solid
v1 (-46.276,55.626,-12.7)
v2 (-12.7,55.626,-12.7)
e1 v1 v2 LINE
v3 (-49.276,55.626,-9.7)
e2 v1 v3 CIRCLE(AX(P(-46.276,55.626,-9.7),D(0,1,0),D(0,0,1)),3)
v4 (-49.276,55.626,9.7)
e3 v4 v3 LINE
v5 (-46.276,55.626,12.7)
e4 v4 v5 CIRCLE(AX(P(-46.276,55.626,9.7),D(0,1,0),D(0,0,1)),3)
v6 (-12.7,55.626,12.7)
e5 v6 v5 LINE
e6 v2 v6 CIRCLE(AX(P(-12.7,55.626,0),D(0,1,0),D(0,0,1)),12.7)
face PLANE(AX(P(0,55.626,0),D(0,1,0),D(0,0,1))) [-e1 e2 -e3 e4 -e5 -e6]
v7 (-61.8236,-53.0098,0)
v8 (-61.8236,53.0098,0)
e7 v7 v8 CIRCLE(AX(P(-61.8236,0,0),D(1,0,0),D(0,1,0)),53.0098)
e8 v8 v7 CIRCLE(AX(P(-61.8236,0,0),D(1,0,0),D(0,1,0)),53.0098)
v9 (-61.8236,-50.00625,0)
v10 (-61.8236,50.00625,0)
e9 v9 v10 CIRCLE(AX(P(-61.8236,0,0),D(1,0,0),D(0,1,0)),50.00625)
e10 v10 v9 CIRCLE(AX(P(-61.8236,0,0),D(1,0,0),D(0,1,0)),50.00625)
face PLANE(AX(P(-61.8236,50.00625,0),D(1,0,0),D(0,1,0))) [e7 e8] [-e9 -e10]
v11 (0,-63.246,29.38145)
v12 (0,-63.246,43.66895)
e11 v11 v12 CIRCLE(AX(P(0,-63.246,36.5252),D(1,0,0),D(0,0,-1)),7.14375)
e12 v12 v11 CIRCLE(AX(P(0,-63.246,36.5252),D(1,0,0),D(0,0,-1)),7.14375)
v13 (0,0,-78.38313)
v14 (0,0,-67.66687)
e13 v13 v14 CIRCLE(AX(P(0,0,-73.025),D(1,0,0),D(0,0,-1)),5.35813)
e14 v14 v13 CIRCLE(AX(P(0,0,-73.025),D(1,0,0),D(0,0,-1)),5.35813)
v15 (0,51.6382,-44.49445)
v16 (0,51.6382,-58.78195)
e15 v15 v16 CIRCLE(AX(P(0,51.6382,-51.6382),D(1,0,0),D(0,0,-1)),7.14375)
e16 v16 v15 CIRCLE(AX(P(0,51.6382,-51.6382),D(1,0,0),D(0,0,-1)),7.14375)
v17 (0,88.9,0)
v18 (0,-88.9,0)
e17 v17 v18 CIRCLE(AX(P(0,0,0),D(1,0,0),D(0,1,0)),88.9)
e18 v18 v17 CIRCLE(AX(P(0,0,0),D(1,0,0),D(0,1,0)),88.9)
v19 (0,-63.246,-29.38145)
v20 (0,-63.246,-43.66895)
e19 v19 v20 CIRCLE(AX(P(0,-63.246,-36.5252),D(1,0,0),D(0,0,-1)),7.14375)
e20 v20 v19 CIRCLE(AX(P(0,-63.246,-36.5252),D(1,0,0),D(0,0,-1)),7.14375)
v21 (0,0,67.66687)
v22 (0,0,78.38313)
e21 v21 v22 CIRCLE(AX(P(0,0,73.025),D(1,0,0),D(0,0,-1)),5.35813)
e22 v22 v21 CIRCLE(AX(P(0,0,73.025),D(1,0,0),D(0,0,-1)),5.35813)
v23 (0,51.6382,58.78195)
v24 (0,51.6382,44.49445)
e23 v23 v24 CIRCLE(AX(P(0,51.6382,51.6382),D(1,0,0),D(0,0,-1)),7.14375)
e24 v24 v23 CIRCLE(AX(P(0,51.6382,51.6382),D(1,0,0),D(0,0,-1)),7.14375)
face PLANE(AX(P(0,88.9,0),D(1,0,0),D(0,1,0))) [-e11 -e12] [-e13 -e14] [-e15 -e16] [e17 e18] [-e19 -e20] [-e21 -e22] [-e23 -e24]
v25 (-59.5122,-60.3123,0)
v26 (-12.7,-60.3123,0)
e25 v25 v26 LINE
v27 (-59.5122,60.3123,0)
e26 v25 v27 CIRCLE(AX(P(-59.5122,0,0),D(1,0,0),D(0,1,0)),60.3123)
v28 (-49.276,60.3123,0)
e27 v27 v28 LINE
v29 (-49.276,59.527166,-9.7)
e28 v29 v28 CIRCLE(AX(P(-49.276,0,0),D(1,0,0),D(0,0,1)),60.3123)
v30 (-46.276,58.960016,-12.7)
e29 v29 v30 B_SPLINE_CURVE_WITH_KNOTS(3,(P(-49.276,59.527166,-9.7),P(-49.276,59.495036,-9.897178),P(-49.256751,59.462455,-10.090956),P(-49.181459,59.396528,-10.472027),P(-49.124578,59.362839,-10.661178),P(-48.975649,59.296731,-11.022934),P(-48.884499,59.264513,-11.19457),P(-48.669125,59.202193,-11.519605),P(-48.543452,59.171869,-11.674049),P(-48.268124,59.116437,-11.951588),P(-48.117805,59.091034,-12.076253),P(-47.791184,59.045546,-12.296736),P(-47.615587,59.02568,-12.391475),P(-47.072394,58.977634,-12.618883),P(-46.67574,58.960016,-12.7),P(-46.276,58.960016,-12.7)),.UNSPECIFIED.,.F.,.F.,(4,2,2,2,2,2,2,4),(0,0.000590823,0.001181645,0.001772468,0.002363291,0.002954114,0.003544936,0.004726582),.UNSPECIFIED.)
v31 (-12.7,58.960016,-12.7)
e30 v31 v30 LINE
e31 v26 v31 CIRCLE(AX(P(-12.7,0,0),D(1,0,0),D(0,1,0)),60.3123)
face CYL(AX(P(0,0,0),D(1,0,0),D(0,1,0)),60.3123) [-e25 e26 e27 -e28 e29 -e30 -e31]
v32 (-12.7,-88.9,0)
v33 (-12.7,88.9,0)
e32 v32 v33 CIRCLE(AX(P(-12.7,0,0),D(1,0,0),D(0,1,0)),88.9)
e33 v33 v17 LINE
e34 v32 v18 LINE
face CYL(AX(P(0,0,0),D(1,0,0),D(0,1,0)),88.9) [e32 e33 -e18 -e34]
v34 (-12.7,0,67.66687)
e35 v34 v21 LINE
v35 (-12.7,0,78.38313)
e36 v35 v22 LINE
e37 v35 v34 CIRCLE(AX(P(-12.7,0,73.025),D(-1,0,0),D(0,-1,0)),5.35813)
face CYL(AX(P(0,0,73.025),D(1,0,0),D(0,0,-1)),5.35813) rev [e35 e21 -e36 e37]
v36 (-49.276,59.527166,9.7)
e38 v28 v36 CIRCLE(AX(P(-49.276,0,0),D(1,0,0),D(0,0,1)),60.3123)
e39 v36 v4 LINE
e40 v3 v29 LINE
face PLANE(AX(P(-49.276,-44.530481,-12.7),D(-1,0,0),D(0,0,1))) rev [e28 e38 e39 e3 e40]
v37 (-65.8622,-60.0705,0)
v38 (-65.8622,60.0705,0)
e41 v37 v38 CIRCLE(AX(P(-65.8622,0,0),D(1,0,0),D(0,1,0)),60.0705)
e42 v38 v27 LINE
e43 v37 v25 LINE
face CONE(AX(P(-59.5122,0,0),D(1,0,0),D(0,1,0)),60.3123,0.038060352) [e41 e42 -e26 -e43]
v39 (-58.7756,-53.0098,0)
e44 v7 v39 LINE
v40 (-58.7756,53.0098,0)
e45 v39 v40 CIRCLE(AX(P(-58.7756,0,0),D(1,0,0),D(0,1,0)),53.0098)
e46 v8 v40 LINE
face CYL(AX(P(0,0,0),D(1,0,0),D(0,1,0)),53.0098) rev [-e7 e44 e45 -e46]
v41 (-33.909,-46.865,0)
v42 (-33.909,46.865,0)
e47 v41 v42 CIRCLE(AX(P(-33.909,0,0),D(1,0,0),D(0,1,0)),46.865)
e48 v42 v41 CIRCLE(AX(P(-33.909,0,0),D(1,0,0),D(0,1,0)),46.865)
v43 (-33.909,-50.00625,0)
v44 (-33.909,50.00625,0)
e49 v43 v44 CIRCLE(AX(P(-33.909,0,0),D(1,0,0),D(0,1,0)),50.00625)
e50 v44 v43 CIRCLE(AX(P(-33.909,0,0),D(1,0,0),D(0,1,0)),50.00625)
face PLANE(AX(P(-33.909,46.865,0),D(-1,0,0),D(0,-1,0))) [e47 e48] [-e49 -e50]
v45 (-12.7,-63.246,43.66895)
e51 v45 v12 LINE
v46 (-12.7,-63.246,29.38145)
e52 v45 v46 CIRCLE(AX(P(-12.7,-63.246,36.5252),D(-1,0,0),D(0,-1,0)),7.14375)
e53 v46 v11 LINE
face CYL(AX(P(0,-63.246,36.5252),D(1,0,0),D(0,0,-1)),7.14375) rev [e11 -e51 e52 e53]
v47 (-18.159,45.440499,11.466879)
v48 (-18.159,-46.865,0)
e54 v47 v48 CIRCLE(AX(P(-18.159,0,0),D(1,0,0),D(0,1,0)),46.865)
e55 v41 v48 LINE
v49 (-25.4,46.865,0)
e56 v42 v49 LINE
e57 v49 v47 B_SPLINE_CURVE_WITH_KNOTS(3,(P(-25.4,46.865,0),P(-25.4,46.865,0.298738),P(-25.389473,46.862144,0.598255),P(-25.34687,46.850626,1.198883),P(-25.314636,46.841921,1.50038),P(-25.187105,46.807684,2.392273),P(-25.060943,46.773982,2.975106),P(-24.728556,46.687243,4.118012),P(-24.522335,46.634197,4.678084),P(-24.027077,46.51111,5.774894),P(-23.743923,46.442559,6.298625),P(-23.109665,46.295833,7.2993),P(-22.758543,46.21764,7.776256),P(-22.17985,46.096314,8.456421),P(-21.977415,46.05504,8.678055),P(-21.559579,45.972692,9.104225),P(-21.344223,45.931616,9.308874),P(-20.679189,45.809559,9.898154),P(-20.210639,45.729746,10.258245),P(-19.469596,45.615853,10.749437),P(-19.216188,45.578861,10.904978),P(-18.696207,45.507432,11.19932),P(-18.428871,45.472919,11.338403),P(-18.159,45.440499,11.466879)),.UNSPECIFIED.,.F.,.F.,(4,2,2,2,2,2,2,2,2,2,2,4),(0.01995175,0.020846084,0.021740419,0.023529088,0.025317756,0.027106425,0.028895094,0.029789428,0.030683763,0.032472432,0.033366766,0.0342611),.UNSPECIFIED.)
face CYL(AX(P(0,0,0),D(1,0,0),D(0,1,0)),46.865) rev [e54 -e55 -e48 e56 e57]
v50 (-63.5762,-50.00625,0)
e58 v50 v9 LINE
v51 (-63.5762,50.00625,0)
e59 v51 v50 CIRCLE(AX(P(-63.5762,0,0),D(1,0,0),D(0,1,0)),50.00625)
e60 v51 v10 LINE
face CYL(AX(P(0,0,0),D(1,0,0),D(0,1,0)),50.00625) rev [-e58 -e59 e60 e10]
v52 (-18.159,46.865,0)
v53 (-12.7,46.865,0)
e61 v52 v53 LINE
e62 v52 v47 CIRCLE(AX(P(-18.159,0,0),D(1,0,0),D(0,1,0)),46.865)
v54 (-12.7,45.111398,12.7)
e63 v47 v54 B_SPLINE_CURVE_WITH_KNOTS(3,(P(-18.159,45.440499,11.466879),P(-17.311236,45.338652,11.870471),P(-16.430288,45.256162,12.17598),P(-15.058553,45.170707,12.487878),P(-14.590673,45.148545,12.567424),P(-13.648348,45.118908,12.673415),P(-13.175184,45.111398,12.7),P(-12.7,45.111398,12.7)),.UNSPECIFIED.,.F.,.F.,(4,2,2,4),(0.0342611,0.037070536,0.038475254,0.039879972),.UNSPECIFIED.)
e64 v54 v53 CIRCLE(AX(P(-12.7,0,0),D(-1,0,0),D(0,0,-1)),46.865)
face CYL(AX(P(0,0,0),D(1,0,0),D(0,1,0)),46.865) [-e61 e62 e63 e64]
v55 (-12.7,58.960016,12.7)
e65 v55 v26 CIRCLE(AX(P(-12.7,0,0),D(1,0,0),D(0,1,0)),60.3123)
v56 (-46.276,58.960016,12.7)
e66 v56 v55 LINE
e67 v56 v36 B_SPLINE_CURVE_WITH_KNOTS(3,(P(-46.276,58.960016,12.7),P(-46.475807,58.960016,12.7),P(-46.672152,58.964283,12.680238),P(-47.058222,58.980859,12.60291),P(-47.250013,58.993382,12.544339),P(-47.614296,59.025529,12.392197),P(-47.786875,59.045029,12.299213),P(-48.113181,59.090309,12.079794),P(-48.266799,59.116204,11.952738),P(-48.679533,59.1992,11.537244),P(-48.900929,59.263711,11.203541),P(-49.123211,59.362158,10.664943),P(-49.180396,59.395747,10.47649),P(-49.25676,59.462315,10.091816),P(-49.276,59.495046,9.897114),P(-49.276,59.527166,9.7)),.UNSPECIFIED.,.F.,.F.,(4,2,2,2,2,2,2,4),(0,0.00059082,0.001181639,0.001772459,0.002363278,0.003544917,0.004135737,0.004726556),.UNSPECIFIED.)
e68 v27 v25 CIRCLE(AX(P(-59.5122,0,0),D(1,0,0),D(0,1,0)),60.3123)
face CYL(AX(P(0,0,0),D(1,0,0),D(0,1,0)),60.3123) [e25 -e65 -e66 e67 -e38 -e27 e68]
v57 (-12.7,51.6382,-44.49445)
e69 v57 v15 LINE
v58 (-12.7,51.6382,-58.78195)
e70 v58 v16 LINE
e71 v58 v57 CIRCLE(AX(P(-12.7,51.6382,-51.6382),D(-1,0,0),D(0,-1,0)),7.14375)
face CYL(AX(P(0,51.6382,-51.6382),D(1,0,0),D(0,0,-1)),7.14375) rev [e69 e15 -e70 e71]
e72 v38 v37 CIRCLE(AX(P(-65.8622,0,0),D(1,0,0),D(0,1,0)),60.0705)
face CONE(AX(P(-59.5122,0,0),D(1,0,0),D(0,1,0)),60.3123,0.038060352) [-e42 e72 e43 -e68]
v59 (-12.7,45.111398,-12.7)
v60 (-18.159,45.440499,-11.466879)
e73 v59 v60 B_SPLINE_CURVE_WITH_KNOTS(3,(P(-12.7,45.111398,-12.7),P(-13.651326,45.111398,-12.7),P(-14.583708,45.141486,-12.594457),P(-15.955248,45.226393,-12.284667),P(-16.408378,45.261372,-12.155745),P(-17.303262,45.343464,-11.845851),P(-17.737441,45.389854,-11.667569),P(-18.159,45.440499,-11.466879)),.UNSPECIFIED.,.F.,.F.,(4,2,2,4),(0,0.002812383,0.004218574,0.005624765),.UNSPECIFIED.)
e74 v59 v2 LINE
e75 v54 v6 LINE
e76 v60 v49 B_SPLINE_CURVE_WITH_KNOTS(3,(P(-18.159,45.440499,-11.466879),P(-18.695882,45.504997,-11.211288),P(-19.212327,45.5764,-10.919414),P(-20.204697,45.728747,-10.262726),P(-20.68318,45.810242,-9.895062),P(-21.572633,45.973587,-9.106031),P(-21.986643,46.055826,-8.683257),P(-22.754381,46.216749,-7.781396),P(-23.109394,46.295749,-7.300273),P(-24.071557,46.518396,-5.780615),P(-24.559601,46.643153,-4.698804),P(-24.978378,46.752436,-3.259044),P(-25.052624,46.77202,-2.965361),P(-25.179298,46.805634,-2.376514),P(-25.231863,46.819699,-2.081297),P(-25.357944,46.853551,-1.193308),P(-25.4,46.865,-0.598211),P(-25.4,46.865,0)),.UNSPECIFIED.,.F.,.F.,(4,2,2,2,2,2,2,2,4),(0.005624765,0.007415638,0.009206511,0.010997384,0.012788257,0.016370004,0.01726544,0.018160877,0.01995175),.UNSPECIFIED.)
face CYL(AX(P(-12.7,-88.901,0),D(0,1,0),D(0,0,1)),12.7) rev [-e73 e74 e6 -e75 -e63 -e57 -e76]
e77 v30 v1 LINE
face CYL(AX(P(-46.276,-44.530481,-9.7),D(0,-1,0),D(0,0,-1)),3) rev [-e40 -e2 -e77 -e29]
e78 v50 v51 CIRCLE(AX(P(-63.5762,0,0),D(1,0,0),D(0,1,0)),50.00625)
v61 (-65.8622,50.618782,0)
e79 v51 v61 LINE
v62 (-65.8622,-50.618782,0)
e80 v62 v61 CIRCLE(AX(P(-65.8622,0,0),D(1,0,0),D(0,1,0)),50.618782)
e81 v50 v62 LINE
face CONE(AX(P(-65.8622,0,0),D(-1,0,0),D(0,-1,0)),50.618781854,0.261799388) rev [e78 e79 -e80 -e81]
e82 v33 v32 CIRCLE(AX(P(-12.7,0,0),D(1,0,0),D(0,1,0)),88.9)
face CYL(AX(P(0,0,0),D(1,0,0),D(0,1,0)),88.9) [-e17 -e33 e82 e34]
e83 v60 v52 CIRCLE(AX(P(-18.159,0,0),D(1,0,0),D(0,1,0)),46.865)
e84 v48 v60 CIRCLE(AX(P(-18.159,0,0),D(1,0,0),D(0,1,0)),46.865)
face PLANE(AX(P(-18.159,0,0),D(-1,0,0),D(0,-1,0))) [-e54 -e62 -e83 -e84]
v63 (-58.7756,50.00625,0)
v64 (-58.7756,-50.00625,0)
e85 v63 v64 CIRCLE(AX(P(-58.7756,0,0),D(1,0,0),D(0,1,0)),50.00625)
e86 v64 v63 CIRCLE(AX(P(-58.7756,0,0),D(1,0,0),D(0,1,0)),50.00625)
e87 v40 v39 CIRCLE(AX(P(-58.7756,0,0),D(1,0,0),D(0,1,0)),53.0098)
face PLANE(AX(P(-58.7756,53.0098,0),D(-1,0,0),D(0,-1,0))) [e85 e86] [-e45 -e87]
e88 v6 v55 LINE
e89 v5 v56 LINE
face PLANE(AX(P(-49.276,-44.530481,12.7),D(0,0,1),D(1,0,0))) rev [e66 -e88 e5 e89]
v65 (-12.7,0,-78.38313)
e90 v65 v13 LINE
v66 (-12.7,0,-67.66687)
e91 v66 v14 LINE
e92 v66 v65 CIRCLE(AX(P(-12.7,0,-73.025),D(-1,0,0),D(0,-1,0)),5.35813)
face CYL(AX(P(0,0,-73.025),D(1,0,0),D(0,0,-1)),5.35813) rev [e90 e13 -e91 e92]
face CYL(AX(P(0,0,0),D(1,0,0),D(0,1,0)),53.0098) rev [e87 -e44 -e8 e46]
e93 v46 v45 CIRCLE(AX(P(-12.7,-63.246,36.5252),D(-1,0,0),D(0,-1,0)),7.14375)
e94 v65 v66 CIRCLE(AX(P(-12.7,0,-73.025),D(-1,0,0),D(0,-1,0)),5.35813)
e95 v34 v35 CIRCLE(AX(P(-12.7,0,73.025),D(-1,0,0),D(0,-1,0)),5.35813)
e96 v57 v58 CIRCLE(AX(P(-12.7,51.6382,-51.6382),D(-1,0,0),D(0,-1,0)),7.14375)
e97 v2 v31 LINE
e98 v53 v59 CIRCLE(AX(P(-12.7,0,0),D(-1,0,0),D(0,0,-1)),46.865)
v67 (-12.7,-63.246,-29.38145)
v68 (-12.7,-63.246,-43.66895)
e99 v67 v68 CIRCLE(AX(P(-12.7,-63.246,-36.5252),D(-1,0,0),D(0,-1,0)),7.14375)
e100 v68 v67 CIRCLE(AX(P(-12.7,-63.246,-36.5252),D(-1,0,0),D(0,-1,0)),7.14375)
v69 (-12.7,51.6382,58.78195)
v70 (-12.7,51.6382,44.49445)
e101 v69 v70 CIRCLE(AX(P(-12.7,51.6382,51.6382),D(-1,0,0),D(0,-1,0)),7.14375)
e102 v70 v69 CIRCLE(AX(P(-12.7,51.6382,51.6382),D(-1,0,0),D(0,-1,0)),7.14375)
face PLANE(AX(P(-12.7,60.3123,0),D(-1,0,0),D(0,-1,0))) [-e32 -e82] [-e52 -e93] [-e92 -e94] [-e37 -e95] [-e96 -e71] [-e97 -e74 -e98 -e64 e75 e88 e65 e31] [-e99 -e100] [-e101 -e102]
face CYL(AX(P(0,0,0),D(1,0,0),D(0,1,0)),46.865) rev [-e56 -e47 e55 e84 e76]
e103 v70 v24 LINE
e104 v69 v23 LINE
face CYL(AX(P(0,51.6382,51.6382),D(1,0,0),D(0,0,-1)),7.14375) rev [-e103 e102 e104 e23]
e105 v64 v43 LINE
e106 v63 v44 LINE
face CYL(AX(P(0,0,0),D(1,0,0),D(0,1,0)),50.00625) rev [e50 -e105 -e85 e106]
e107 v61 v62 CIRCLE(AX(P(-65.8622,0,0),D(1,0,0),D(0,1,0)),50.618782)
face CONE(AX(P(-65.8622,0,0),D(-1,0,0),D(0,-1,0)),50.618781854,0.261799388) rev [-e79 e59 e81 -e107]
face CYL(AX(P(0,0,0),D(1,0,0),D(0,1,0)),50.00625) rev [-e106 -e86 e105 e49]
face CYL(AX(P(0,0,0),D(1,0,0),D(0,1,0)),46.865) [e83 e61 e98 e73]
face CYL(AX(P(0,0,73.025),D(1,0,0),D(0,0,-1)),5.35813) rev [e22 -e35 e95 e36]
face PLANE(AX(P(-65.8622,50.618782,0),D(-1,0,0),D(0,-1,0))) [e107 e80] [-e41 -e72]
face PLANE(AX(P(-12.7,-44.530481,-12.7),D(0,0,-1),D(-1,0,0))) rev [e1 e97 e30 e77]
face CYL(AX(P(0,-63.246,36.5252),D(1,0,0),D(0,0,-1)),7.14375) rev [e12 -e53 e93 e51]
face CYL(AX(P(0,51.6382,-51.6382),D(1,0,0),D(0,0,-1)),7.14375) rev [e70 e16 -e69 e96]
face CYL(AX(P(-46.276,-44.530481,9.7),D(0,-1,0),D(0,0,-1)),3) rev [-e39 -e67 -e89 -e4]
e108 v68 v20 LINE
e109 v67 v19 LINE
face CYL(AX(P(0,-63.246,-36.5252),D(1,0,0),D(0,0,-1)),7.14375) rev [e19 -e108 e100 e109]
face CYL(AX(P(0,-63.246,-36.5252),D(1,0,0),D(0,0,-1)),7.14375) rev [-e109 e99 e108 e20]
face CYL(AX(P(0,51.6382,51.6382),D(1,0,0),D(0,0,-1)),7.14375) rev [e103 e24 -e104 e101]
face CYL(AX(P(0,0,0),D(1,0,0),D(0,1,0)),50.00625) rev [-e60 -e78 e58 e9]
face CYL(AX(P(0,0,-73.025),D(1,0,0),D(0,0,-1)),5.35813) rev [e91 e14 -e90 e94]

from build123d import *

# Parameters (mm, degrees)
F_9_16_0_5625_DIAMETER_HOLE1_D = 14.2875
F_1_2_13_TAPPED_HOLE1_D        = 10.71626
EXTRUDE1_START                 = 55.626
SKETCH8_W                      = 36.576
SKETCH8_H                      = 25.4
EXTRUDE1_DEPTH                 = 4.6863
EXTRUDE2_REACH                 = 184.013
EXTRUDE2_END_RADIUS            = 46.865
FILLET1_R                      = 3


with BuildPart() as part:
    # Sketch1 → Revolve1 (revolve)
    with BuildSketch(Plane.XY):
        Polygon((-65.8622, 50.618781854), (-65.8622, 60.0705), (-59.5122, 60.3123), (-12.7, 60.3123), (-12.7, 88.9), (0, 88.9), (0, 0), (-18.159, 0), (-18.159, 46.865), (-33.909, 46.865), (-33.909, 50.00625), (-58.7756, 50.00625), (-58.7756, 53.0098), (-61.8236, 53.0098), (-61.8236, 50.00625), (-63.5762, 50.00625), align=None)
    revolve(axis=Axis((0, 0, 0), (-1, 0, 0)))

    # 9/16 (0.5625) Diameter Hole1 (through all)
    with Locations(Plane(origin=(0, 0, 0), x_dir=(0, 0, -1), z_dir=(1, 0, 0))):
        with Locations((-51.6382, 51.6382), (51.6382, 51.6382), (-36.5252, -63.246), (36.5252, -63.246)):
            Hole(F_9_16_0_5625_DIAMETER_HOLE1_D / 2)

    # 1/2-13 Tapped Hole1 (through all)
    with Locations(Plane(origin=(0, 0, 0), x_dir=(0, 0, -1), z_dir=(1, 0, 0))):
        with Locations((-73.025, 0), (73.025, 0)):
            Hole(F_1_2_13_TAPPED_HOLE1_D / 2)

    # Sketch8 → Extrude1 (cut)
    with BuildSketch(Plane(origin=(0, 0, 0), x_dir=(1, 0, 0), z_dir=(0, 1, 0)).offset(EXTRUDE1_START)):
        with Locations((-30.988, 0)):
            Rectangle(SKETCH8_W, SKETCH8_H)
    extrude(amount=EXTRUDE1_DEPTH, mode=Mode.SUBTRACT)

    # Extrude2: up to this cylinder (the profile starts outside it)
    extrude2_end = Plane(origin=(-18.090047, 0, 0), z_dir=(1, 0, 0)) * Cylinder(EXTRUDE2_END_RADIUS, 462.756, mode=Mode.PRIVATE)
    # Sketch9 → Extrude2 (cut, up to the surface)
    with BuildSketch(Plane(origin=(0, 55.626, 0), x_dir=(1, 0, 0), z_dir=(0, 1, 0)), mode=Mode.PRIVATE) as extrude2_sk1:
        with BuildLine():
            Line((-12.7, 12.7), (-12.7, -12.7))
            ThreePointArc((-12.7, -12.7), (-25.4, 0), (-12.7, 12.7))
        make_face()
    extrude2_tool1 = extrude(extrude2_sk1.sketch, amount=-EXTRUDE2_REACH, mode=Mode.PRIVATE) - extrude2_end
    add(extrude2_tool1.solids().sort_by_distance((-18.090047, 55.626, 0))[0], mode=Mode.SUBTRACT)

    # Fillet1
    fillet1_edges = [part.edges().sort_by_distance(p)[0] for p in [
        (-49.276, 57.293008189, 12.7),
        (-49.276, 57.293008189, -12.7),
    ]]
    fillet(fillet1_edges, radius=FILLET1_R)


solid = part.part
